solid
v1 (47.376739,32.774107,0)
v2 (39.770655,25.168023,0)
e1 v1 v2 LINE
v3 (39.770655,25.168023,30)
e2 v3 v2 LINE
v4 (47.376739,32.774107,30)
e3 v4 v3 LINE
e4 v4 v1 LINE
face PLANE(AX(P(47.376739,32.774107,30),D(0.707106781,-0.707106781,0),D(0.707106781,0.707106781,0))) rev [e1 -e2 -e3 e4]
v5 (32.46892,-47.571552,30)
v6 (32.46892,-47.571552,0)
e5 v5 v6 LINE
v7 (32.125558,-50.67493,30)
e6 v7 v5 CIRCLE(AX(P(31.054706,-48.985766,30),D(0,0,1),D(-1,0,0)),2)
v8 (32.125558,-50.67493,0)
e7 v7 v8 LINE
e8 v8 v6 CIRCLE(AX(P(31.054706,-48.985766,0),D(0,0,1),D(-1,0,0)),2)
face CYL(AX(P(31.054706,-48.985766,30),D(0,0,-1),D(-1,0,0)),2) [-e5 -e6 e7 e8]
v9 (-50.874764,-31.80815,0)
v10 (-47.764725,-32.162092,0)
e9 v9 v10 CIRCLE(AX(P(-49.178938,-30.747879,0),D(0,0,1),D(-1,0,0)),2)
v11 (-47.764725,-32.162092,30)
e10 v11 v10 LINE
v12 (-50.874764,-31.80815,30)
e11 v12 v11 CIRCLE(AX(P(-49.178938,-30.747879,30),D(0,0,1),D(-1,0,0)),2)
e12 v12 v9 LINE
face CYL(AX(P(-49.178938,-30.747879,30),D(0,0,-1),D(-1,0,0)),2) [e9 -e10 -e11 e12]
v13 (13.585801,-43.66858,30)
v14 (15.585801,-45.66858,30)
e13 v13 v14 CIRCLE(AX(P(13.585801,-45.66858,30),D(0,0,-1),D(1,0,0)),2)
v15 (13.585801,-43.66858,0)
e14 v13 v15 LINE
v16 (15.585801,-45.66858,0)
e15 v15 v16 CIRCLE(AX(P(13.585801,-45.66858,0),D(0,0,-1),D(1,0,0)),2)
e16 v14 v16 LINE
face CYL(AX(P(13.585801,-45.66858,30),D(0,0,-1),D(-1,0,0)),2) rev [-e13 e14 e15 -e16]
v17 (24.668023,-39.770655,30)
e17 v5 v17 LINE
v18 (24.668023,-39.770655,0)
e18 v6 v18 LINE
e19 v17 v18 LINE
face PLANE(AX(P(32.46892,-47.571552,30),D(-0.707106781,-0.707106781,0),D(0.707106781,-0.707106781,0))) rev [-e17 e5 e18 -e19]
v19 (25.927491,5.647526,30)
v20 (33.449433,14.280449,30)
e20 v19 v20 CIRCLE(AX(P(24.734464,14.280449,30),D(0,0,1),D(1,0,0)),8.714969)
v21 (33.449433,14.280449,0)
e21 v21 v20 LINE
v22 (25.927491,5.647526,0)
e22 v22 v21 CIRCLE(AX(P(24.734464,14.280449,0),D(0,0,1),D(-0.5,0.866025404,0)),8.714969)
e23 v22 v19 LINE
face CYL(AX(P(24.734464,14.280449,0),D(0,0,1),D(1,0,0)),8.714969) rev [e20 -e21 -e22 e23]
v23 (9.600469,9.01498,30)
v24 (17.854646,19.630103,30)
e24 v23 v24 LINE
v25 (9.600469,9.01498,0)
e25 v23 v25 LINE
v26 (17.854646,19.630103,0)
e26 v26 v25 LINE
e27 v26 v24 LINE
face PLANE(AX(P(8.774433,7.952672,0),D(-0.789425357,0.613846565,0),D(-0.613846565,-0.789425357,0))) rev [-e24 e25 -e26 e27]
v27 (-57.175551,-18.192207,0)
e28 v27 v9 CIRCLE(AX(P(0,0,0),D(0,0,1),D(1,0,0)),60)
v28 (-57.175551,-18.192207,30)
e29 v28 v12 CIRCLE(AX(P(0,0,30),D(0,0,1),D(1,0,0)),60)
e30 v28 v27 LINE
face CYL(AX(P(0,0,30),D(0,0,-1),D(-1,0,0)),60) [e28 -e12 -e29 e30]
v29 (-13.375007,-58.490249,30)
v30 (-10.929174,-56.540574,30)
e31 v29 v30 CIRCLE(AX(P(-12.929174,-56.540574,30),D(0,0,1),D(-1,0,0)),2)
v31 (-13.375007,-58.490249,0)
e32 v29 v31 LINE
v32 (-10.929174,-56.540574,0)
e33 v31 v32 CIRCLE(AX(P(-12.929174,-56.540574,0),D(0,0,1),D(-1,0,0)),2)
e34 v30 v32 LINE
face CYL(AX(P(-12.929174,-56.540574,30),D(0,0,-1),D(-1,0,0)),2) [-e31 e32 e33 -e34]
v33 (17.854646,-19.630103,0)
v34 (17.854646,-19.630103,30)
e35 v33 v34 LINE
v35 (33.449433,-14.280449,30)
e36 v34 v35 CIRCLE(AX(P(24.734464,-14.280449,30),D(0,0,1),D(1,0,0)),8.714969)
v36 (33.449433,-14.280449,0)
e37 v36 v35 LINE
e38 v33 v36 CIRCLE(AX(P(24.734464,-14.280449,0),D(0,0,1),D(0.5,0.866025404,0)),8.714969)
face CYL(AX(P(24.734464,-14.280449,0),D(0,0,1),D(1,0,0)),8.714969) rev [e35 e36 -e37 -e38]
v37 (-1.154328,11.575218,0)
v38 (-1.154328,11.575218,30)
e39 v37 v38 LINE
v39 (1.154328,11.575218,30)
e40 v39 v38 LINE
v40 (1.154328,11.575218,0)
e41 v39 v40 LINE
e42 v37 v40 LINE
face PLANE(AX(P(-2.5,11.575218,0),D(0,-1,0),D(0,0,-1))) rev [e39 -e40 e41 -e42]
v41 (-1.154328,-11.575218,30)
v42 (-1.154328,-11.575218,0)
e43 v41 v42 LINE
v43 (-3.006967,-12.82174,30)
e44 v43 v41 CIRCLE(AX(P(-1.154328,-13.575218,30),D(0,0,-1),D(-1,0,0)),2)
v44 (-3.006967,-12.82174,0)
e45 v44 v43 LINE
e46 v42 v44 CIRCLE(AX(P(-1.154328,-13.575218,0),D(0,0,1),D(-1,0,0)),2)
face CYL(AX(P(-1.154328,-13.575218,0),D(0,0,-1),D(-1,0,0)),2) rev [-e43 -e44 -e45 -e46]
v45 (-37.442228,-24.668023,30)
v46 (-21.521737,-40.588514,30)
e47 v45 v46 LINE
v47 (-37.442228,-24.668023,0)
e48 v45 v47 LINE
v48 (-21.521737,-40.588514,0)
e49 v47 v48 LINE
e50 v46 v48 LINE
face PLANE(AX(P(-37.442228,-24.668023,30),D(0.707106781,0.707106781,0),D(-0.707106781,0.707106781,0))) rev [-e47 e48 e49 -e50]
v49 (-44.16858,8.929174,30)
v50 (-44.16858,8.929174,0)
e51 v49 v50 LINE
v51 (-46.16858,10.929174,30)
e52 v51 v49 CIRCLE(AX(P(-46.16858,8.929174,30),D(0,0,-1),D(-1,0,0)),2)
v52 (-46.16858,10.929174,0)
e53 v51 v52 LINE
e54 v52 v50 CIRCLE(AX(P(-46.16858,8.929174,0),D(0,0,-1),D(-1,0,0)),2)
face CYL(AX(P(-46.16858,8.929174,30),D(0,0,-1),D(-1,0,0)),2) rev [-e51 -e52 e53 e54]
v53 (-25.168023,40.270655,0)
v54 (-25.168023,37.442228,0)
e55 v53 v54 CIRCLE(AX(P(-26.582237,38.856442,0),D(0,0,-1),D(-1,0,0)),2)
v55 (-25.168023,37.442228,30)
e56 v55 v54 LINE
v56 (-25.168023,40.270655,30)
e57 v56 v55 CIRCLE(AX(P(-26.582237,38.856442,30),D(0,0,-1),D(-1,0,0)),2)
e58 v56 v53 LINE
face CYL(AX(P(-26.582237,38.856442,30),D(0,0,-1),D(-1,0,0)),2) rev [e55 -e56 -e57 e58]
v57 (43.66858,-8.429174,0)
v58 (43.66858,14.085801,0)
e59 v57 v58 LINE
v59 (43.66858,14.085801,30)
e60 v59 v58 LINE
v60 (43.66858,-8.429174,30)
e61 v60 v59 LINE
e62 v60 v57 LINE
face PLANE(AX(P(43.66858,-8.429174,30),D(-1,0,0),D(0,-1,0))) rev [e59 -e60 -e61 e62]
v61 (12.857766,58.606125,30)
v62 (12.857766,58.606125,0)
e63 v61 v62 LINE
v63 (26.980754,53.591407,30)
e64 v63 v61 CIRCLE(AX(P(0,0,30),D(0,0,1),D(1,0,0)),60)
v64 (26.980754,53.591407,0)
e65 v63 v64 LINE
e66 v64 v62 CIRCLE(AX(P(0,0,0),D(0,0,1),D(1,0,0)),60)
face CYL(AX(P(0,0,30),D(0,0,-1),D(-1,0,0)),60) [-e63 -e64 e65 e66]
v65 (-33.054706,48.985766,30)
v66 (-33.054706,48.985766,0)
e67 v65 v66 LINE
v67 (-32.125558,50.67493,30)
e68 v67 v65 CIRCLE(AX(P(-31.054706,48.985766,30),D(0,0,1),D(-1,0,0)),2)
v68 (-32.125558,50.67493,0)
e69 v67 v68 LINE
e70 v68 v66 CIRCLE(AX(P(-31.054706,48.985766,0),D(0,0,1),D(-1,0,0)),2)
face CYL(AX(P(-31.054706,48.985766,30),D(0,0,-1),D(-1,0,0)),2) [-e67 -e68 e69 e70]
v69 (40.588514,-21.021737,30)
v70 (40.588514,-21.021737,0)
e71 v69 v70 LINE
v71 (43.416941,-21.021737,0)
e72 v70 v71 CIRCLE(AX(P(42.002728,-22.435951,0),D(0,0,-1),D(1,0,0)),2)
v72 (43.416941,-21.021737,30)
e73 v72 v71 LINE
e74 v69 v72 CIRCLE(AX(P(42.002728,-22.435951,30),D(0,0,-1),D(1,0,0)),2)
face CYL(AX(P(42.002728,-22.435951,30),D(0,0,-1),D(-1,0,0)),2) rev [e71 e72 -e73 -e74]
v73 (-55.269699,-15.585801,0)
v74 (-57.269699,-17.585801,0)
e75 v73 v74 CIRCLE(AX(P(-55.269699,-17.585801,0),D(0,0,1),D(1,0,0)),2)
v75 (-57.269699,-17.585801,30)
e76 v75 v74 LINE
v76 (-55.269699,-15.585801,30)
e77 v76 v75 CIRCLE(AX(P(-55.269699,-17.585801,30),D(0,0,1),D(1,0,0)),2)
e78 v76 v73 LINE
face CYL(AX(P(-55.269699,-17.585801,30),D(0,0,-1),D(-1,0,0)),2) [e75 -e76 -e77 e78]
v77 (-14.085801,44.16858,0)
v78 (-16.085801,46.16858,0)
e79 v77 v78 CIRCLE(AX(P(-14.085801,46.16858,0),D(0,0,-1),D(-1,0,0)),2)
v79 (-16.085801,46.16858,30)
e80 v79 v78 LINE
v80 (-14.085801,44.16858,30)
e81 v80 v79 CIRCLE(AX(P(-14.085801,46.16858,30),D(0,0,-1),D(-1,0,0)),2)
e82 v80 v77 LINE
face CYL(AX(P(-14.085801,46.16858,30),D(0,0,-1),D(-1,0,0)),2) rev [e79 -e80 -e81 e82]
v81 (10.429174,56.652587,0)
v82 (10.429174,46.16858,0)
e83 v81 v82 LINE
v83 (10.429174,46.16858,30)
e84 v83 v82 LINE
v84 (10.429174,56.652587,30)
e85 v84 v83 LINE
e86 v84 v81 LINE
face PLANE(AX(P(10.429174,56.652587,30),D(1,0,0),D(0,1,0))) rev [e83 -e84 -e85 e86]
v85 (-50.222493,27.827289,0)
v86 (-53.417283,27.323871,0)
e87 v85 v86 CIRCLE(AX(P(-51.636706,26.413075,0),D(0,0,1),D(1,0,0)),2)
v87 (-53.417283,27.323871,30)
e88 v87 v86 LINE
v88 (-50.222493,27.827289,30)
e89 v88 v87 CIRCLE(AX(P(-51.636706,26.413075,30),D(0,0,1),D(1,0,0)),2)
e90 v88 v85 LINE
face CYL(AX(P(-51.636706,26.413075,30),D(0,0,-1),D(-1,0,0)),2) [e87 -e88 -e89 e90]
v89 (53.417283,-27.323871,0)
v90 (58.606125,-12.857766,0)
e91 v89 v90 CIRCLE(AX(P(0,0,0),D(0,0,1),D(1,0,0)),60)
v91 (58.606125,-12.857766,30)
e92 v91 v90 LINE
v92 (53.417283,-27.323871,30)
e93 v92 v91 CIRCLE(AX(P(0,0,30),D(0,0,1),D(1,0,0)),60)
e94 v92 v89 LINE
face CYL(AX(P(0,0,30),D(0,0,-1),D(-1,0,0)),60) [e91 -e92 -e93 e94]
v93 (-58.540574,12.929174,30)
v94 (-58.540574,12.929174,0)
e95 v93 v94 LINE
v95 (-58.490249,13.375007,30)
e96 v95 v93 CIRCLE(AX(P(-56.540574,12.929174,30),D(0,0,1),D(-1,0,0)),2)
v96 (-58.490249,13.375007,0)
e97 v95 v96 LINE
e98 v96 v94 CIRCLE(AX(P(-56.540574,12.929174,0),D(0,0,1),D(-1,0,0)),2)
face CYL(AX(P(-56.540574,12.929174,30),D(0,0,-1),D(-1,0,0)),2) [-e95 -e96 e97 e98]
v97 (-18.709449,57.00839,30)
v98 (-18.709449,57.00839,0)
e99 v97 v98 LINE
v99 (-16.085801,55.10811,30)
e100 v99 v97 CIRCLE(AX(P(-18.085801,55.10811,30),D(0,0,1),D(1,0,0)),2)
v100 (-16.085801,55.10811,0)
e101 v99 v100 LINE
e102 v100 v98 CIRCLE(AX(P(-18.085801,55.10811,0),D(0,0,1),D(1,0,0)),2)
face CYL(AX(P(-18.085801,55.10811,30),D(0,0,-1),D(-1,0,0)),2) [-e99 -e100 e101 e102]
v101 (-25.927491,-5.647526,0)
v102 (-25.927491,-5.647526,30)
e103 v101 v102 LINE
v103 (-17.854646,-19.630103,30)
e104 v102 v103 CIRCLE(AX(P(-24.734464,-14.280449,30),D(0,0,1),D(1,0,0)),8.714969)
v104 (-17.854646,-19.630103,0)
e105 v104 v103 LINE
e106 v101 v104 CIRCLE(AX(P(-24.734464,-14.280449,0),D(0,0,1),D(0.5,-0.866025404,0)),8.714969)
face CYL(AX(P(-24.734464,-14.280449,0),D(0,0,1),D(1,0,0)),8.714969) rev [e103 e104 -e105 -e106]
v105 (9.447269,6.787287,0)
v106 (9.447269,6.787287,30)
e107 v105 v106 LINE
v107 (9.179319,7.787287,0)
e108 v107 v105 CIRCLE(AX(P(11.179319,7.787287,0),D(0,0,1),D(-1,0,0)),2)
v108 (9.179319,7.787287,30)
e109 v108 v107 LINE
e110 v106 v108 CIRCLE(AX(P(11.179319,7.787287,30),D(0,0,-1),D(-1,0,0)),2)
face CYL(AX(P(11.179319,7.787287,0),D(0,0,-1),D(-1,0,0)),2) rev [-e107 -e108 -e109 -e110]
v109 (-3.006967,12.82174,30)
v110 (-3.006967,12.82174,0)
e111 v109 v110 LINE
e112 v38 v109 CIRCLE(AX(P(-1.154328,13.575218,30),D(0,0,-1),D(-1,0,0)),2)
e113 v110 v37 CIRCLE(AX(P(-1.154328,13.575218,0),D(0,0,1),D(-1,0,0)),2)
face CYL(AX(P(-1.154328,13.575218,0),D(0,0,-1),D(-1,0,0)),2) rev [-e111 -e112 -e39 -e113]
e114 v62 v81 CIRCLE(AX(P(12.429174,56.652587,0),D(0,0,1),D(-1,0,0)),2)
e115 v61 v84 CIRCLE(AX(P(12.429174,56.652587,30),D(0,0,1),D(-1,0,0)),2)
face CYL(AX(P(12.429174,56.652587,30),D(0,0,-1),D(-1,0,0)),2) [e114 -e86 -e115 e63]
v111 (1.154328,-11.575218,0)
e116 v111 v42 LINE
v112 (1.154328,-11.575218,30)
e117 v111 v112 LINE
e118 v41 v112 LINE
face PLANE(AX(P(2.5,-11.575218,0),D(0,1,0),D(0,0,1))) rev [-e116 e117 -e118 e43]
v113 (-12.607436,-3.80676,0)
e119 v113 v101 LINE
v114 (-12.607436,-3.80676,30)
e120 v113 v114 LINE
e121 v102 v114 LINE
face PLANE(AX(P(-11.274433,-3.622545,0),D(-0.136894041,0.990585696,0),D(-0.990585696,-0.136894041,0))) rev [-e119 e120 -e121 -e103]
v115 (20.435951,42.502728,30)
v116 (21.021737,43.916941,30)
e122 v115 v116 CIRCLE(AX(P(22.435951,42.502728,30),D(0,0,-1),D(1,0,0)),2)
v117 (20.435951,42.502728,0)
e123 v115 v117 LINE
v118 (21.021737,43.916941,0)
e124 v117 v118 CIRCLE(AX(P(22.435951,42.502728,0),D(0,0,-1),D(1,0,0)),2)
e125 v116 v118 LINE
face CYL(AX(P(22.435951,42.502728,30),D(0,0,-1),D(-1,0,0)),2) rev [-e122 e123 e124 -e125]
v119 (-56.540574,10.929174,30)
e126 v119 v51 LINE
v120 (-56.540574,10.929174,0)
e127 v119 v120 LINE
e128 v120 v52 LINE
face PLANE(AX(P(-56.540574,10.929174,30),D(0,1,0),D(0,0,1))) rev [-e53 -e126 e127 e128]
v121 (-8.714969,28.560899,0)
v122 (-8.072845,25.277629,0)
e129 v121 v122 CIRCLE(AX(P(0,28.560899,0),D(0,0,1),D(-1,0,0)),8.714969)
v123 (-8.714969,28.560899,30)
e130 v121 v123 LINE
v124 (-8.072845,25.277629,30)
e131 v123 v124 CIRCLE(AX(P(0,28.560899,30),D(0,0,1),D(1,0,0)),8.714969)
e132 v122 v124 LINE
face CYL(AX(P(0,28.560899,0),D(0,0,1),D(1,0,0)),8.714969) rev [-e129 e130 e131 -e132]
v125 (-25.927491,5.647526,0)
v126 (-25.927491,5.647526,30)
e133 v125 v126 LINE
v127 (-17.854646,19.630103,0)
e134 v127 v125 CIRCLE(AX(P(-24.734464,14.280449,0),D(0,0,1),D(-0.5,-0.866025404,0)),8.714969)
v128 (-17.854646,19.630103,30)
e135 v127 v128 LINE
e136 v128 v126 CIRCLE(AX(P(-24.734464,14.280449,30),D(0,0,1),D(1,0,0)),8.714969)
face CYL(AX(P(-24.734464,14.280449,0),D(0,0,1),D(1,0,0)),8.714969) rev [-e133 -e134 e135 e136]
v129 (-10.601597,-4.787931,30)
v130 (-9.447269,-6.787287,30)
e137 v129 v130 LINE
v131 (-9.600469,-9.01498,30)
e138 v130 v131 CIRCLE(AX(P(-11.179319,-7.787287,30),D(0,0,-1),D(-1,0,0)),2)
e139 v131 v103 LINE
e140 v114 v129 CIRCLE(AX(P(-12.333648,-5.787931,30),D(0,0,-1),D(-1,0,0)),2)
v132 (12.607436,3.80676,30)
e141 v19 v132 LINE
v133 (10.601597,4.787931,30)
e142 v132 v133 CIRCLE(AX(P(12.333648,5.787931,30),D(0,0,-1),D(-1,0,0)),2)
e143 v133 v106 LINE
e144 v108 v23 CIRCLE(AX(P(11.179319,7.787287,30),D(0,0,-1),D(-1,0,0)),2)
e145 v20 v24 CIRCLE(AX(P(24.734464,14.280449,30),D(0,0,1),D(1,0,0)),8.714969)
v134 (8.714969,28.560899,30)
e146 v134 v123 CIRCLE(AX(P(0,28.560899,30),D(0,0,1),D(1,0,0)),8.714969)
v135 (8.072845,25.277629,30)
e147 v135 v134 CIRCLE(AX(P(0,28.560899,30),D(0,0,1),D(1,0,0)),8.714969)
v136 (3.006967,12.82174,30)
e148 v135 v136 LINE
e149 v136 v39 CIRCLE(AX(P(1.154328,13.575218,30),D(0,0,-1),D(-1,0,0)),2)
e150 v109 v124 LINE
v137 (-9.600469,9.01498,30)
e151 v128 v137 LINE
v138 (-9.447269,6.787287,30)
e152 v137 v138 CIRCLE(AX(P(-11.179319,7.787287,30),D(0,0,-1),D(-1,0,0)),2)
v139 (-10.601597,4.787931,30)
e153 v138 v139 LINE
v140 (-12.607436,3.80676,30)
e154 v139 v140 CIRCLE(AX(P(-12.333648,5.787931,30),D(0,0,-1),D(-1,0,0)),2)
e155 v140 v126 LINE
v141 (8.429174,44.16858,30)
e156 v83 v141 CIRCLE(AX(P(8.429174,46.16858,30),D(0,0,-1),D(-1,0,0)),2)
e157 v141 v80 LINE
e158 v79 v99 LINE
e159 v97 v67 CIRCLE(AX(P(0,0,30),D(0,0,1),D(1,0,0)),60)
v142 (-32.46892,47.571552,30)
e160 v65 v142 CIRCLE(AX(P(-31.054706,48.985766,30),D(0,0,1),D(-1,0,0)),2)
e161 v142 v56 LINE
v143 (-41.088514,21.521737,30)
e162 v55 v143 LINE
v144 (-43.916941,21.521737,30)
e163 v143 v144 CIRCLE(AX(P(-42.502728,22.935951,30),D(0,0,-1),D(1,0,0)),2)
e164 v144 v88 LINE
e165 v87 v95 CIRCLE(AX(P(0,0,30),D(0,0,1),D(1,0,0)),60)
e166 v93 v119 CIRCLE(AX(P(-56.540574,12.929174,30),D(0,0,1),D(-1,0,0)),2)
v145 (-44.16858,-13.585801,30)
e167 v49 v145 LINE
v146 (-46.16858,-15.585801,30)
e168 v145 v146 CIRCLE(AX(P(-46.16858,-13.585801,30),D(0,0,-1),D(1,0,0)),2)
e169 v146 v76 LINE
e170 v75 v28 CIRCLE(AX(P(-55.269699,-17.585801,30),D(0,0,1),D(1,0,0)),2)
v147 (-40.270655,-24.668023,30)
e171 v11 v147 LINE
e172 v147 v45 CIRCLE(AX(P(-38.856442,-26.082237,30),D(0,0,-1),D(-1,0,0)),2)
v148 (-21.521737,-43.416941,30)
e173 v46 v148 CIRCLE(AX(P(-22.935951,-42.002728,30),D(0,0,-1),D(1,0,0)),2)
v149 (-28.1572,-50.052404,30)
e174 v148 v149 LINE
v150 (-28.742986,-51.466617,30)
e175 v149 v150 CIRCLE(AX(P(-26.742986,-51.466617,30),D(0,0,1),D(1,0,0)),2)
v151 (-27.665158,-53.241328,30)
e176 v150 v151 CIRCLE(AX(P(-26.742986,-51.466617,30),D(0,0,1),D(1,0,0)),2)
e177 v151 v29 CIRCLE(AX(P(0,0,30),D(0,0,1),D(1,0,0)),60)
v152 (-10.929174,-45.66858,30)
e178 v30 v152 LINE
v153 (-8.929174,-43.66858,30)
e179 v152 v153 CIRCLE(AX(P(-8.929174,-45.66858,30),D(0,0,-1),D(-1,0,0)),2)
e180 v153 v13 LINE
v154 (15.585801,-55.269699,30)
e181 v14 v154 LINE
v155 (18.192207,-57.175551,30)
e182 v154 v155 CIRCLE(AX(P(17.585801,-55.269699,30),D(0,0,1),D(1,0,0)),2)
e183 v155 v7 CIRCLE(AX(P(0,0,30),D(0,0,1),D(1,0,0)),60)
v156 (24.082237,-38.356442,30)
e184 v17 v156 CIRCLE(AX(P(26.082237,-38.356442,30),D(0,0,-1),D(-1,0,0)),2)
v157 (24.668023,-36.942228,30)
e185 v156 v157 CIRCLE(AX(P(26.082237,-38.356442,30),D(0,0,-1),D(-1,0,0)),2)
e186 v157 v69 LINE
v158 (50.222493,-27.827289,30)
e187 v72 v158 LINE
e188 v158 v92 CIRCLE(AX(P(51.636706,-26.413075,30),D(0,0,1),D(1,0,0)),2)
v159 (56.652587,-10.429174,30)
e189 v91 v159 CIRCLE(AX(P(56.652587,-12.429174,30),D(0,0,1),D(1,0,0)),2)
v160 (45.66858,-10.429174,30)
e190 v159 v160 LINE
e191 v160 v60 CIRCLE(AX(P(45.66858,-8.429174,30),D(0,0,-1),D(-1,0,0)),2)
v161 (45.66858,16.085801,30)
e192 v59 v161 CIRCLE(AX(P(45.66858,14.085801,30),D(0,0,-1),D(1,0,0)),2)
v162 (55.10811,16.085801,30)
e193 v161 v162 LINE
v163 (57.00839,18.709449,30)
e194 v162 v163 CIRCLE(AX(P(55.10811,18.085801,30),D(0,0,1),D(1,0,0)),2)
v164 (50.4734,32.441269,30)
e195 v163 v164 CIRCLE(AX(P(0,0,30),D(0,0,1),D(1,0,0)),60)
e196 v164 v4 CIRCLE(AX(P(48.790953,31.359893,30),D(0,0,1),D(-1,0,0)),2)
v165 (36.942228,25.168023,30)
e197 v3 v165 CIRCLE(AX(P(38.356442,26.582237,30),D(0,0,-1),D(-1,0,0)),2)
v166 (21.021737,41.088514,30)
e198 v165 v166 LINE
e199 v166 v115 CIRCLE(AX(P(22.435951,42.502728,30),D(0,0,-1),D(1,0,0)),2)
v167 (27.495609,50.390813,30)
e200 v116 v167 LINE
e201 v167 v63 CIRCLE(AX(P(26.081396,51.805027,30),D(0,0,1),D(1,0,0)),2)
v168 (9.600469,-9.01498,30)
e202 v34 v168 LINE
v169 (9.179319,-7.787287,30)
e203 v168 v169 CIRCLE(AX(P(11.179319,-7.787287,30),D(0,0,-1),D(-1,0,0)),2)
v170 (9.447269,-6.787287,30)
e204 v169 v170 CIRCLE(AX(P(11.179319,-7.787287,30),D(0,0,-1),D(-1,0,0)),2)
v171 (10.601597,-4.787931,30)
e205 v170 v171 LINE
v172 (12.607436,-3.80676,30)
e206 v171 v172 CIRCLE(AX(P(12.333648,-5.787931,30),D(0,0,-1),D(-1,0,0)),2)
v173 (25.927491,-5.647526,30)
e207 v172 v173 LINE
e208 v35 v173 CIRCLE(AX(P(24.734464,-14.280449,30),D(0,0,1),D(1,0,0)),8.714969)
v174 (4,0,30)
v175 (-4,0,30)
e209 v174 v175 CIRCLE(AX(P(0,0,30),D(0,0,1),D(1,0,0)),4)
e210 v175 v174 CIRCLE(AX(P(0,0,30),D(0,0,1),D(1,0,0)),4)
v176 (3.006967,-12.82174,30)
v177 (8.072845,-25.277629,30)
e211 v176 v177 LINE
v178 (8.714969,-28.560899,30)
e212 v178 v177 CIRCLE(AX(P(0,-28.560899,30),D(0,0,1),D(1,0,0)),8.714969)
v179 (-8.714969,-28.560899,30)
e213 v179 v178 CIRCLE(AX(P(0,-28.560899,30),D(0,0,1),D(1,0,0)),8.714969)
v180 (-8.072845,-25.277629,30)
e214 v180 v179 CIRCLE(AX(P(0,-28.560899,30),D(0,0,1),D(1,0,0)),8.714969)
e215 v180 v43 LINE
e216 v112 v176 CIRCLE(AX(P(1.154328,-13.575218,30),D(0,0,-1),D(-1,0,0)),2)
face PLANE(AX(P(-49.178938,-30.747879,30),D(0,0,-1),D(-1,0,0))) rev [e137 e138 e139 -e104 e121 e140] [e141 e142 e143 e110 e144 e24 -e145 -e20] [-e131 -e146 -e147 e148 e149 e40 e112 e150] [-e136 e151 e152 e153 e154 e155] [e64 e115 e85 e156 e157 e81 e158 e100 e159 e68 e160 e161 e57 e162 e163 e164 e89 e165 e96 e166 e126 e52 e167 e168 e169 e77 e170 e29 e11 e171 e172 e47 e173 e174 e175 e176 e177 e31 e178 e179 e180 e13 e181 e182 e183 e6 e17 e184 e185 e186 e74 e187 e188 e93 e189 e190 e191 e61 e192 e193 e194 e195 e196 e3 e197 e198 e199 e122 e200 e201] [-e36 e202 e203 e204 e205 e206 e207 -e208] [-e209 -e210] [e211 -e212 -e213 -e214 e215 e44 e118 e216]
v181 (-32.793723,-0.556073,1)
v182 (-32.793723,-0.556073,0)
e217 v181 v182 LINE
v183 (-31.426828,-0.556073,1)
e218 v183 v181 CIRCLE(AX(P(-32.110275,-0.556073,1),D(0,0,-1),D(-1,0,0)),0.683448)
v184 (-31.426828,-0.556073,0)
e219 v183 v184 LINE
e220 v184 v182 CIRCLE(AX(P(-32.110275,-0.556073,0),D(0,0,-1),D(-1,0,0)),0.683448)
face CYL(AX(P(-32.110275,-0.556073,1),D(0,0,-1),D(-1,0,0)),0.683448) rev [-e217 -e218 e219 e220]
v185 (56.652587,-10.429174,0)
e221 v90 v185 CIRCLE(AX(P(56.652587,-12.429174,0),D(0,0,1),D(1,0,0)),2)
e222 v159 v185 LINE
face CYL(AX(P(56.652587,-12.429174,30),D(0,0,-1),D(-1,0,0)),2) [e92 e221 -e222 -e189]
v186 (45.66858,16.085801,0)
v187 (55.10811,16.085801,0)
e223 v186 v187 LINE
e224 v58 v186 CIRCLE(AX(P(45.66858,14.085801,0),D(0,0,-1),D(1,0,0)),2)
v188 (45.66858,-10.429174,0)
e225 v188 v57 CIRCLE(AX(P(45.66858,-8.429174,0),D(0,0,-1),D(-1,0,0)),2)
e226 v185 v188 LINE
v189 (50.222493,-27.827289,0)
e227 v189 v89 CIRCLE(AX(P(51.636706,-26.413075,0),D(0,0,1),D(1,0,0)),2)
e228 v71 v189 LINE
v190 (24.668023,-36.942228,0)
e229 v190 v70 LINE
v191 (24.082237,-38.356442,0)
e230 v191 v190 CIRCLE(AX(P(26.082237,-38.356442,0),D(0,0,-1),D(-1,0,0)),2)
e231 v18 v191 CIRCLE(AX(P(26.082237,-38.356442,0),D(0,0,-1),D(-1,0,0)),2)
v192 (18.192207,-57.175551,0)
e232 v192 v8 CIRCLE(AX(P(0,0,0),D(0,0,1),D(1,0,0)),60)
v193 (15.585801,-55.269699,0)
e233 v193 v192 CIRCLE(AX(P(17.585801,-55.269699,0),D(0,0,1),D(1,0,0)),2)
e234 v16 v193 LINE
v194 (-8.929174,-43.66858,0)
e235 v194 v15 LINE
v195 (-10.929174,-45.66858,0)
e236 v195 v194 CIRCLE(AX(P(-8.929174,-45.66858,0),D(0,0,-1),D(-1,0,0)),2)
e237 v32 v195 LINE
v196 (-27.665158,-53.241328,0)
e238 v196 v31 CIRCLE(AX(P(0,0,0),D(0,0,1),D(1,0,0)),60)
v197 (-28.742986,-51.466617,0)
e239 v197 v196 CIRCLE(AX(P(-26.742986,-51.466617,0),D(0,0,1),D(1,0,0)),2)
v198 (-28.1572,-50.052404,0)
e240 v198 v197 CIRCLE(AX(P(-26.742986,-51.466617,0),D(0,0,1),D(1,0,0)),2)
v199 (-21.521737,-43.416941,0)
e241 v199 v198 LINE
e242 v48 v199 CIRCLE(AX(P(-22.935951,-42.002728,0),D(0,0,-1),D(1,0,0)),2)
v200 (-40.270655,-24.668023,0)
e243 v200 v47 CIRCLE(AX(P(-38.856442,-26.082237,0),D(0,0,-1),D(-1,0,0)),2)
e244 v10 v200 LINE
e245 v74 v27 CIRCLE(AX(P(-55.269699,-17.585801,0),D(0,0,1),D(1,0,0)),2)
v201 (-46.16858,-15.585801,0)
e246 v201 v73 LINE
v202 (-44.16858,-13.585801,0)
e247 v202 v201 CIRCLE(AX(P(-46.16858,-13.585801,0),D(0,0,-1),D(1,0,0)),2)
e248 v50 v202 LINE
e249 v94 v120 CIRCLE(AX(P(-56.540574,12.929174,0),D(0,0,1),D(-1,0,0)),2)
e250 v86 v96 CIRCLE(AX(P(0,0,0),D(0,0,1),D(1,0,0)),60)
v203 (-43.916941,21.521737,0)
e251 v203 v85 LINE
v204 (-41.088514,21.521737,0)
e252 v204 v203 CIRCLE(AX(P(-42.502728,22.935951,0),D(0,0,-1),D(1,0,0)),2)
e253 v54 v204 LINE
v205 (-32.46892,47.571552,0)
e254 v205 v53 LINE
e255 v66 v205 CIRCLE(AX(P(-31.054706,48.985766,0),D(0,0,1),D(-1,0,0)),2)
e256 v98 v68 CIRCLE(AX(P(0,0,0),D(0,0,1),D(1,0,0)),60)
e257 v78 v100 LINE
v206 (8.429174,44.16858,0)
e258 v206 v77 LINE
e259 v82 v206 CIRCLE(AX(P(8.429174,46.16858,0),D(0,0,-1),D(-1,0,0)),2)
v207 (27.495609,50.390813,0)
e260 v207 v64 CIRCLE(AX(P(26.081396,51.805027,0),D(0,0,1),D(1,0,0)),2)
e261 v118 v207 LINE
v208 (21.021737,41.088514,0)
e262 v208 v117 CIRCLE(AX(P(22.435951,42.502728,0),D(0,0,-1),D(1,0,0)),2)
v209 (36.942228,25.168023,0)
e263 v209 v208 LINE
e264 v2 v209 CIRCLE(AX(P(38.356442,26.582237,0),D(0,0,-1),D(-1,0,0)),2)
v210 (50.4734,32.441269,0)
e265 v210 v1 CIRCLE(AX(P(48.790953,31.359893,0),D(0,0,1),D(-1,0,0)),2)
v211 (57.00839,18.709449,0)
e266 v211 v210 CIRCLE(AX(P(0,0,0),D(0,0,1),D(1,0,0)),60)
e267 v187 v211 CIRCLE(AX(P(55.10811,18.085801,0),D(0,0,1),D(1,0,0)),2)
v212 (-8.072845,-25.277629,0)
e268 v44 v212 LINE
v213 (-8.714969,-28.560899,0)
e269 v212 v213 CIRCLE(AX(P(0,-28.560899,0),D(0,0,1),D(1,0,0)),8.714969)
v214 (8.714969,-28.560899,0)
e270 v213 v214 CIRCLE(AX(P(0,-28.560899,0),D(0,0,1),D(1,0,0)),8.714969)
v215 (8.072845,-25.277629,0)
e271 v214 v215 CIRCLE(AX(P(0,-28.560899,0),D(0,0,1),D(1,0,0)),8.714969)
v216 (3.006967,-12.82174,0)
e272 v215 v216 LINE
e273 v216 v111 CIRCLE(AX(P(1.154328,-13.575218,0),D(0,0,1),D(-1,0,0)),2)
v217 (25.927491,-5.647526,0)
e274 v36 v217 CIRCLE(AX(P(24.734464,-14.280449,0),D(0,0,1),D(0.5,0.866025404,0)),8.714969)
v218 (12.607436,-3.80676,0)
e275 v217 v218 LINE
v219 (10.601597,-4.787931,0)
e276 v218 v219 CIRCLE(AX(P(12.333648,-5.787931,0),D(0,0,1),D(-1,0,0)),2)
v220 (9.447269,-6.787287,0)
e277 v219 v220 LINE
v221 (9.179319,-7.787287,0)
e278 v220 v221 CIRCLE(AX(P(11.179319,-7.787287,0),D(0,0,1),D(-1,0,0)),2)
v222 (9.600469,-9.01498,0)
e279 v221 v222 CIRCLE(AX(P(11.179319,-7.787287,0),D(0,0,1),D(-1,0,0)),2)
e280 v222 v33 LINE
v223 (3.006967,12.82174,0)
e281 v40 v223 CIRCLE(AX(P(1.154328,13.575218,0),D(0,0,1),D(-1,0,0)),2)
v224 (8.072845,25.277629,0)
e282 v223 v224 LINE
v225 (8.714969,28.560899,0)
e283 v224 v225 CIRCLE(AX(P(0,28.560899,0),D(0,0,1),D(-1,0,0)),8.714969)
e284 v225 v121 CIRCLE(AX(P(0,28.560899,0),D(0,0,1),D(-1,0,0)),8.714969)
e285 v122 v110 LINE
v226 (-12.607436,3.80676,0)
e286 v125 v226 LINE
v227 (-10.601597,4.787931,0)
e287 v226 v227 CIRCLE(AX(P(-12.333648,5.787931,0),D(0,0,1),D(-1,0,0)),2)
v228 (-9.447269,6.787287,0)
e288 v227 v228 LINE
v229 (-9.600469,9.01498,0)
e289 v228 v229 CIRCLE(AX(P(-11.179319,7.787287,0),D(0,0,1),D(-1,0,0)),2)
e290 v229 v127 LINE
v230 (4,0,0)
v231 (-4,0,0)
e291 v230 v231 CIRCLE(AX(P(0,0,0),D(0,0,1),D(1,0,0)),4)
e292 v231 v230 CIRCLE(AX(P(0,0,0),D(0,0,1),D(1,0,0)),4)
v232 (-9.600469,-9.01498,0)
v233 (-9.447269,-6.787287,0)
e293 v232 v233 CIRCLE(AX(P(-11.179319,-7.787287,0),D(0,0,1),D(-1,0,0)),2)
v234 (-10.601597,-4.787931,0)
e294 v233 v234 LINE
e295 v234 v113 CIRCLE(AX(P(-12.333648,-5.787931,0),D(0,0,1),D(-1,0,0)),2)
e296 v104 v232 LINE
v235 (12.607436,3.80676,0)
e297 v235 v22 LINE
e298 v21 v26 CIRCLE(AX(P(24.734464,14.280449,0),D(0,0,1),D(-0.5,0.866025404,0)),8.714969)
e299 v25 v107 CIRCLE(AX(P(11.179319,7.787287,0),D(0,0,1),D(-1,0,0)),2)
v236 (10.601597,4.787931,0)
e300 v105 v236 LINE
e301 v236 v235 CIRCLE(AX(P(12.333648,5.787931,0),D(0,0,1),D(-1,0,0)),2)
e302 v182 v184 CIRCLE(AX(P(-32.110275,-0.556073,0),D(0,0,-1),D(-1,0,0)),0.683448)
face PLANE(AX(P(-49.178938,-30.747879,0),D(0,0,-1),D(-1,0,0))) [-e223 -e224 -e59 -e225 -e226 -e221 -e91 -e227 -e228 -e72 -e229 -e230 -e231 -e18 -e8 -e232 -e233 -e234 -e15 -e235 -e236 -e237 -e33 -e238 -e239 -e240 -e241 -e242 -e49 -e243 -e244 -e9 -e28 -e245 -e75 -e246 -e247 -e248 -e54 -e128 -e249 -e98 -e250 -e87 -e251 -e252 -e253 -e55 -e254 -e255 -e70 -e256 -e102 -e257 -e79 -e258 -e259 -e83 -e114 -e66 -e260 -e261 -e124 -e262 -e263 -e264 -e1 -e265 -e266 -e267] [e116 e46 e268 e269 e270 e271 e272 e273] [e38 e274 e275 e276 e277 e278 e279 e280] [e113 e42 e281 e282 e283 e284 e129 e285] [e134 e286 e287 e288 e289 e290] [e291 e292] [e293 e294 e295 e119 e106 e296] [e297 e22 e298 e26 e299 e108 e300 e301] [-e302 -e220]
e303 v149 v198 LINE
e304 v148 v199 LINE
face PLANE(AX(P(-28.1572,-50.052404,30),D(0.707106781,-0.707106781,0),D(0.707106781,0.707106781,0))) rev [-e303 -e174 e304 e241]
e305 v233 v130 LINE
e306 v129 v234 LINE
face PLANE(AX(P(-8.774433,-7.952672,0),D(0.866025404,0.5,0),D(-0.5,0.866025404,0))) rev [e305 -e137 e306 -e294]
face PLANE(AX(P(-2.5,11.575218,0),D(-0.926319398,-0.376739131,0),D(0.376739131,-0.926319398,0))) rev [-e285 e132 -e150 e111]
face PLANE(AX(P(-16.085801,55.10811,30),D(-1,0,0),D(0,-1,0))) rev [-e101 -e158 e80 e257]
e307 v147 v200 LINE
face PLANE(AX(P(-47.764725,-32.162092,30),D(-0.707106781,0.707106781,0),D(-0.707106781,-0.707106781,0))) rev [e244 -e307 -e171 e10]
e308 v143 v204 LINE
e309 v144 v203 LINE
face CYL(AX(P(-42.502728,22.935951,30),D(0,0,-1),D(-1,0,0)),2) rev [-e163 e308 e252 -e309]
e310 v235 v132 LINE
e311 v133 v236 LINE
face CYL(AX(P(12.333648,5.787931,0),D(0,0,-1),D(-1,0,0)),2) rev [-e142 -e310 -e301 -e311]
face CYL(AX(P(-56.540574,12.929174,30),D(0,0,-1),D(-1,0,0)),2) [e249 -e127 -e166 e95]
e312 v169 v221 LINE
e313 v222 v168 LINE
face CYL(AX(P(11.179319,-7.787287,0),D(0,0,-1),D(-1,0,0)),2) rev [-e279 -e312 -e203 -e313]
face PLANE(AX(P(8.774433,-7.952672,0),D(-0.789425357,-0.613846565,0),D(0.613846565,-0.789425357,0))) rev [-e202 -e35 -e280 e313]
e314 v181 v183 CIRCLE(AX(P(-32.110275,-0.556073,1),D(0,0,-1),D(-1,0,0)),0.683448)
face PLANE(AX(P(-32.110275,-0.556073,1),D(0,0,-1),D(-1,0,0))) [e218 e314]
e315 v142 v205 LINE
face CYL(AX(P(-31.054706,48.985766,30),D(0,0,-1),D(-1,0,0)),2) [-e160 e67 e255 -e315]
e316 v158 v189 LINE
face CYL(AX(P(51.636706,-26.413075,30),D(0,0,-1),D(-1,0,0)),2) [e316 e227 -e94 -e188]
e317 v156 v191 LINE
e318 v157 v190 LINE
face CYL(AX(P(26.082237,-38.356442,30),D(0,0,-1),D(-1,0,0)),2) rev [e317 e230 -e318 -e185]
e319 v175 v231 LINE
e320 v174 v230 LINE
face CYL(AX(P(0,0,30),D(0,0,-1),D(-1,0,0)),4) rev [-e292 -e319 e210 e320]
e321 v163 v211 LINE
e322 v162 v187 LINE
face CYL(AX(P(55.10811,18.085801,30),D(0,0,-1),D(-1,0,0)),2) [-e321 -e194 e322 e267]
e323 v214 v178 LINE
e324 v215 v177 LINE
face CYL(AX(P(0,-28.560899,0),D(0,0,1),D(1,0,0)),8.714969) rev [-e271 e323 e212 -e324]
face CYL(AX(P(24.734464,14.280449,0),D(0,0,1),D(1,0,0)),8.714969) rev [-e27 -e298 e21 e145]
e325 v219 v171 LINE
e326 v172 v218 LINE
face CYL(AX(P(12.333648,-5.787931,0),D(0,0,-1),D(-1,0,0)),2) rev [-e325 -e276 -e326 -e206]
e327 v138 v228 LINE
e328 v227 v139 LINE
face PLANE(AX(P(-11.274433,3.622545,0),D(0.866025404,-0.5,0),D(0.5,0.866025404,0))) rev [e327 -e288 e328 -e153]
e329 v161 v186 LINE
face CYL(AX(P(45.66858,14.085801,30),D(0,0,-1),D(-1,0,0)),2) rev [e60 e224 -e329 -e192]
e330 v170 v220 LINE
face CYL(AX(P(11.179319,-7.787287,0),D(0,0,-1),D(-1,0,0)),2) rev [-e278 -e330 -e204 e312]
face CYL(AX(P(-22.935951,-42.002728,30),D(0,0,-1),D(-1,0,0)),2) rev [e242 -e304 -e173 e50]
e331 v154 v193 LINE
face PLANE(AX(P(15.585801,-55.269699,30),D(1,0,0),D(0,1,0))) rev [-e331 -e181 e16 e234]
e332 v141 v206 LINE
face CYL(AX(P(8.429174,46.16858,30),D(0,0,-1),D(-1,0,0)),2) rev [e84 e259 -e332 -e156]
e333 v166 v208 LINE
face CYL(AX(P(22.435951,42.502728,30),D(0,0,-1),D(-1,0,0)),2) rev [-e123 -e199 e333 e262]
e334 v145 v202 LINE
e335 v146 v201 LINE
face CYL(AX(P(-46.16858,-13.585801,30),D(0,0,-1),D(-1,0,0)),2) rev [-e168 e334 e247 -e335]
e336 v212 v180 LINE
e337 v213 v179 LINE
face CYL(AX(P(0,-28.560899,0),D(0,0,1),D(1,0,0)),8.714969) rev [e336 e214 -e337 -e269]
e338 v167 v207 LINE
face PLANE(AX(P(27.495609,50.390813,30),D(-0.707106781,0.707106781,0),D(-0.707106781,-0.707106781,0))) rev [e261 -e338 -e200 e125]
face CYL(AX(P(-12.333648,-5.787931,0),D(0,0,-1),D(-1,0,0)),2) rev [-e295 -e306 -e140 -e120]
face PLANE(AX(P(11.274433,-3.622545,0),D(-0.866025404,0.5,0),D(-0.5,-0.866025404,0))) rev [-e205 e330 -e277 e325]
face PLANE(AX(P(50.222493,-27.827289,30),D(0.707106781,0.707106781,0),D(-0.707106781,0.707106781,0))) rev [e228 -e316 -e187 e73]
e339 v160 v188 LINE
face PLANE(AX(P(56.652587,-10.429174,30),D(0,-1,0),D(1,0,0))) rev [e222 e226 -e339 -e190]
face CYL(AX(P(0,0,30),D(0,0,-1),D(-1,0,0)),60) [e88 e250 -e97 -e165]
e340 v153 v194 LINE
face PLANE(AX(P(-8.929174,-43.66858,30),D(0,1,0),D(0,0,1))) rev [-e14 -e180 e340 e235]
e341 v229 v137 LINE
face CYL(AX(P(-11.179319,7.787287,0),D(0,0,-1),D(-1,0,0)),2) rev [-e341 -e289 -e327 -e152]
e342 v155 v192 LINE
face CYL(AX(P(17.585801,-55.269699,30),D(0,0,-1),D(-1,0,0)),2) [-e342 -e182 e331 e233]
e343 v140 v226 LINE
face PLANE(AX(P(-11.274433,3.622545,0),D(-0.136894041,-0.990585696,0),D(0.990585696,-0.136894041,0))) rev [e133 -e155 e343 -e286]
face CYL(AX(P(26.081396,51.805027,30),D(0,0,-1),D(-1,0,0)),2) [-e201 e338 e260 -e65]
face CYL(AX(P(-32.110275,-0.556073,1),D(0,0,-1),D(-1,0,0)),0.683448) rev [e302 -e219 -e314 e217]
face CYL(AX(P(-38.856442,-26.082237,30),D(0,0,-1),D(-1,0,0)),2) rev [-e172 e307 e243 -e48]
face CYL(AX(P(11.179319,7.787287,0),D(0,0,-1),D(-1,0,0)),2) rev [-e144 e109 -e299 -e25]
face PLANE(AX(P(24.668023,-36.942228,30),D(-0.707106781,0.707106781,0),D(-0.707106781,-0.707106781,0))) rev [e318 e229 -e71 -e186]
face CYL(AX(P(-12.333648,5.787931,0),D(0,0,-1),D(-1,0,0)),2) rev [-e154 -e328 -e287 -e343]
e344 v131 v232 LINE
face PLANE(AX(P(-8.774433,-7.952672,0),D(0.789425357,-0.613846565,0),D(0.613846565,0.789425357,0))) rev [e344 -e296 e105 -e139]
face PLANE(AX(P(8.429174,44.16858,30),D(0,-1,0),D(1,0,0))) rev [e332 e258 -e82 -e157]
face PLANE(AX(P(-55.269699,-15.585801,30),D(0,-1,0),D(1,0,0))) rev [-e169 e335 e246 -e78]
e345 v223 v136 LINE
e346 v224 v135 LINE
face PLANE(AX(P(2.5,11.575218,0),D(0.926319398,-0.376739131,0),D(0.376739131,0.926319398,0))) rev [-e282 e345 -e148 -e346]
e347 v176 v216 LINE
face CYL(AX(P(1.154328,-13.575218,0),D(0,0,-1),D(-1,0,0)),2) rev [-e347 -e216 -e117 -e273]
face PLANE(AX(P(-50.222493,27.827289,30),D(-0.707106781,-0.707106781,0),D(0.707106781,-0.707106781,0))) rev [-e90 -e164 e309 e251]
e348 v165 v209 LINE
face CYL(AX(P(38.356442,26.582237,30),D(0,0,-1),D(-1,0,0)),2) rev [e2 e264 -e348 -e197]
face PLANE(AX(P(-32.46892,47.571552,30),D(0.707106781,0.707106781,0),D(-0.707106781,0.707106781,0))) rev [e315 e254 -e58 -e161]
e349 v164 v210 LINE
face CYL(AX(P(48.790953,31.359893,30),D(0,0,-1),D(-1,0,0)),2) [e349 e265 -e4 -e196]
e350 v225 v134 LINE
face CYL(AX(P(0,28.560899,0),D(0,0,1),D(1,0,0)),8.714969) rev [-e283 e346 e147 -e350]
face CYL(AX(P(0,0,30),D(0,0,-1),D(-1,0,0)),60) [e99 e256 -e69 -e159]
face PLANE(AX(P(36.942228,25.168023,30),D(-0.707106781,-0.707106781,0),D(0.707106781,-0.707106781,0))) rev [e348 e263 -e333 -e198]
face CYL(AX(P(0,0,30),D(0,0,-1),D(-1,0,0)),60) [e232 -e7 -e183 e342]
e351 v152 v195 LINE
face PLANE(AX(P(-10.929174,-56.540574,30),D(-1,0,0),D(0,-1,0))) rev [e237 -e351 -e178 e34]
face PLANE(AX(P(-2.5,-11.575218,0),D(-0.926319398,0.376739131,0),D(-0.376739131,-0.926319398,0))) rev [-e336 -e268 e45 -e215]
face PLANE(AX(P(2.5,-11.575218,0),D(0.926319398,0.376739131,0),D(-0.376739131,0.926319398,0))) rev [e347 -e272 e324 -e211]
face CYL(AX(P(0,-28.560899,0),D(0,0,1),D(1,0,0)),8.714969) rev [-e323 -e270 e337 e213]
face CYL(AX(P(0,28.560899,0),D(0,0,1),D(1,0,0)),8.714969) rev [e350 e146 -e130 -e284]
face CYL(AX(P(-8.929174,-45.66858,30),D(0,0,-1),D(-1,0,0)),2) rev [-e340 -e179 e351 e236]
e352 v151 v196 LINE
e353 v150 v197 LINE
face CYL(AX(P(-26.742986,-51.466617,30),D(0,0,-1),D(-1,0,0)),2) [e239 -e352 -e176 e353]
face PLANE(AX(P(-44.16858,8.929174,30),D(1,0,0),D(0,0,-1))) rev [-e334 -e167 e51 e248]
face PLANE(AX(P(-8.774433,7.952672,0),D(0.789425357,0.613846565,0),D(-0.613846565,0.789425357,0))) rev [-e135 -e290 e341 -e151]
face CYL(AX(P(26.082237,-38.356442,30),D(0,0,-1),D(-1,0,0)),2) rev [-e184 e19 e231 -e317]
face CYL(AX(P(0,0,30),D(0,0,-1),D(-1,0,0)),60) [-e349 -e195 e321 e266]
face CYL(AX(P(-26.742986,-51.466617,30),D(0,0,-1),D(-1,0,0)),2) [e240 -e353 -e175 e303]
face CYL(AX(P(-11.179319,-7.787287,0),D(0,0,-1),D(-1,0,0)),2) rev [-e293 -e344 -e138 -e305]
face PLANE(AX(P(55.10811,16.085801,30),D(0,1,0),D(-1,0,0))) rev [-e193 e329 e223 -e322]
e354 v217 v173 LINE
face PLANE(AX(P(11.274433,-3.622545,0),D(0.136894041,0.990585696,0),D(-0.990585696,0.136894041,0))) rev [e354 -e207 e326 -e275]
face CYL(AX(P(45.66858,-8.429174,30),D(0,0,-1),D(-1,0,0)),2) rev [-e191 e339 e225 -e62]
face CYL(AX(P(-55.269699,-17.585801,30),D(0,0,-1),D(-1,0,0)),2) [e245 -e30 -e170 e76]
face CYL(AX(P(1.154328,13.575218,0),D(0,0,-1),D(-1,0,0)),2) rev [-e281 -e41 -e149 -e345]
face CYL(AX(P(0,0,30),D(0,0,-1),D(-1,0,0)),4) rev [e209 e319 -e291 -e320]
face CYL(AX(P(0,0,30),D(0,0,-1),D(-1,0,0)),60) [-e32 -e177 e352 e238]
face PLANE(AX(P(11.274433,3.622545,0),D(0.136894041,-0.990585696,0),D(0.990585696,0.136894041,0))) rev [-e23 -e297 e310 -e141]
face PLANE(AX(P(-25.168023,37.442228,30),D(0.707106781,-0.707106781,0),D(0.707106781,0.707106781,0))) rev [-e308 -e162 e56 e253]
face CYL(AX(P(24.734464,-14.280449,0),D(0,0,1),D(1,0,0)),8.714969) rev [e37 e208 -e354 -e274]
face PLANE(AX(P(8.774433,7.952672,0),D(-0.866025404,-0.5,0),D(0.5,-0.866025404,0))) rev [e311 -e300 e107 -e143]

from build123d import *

# Parameters (mm, degrees)
SKETCH1_R                = 4
BOSS_EXTRUDE2_DEPTH      = 30
CUT_EXTRUDE2_DEPTH       = 89.20573662
FILLET1_R                = 2
CIRPATTERN1_COUNT        = 6
FILLET1_OF_CIRPATTERN1_R = 2
SKETCH12_R               = 0.68344787
CUT_EXTRUDE4_DEPTH       = 1


with BuildPart() as part:
    # Sketch1 → Boss-Extrude2 (new body)
    with BuildSketch(Plane.XY):
        with BuildLine():
            Line((10.429173845, 56.65258721), (10.429173845, 46.168579918))
            ThreePointArc((10.429173845, 46.168579918), (9.843387407, 44.754366355), (8.429173845, 44.168579918))
            Line((8.429173845, 44.168579918), (-14.085800573, 44.168579918))
            ThreePointArc((-14.085800573, 44.168579918), (-15.500014135, 44.754366355), (-16.085800573, 46.168579918))
            Line((-16.085800573, 46.168579918), (-16.085800573, 55.108110271))
            ThreePointArc((-16.085800573, 55.108110271), (-16.912620406, 56.727878247), (-18.709448869, 57.008389935))
            ThreePointArc((-18.709448869, 57.008389935), (-25.61401293, 54.257924229), (-32.125557949, 50.67492996))
            ThreePointArc((-32.125557949, 50.67492996), (-33.042575786, 49.205706038), (-32.46891958, 47.571552066))
            Line((-32.46891958, 47.571552066), (-25.168022999, 40.270655485))
            ThreePointArc((-25.168022999, 40.270655485), (-24.582236562, 38.856441923), (-25.168022999, 37.44222836))
            Line((-25.168022999, 37.44222836), (-41.088514088, 21.521737271))
            ThreePointArc((-41.088514088, 21.521737271), (-42.50272765, 20.935950834), (-43.916941213, 21.521737271))
            Line((-43.916941213, 21.521737271), (-50.22249286, 27.827288919))
            ThreePointArc((-50.22249286, 27.827288919), (-51.948014566, 28.38869861), (-53.417282506, 27.323871059))
            ThreePointArc((-53.417282506, 27.323871059), (-56.386758875, 20.506911606), (-58.490248558, 13.375007425))
            ThreePointArc((-58.490248558, 13.375007425), (-58.10448971, 11.682511734), (-56.540573606, 10.929173845))
            Line((-56.540573606, 10.929173845), (-46.168579918, 10.929173845))
            ThreePointArc((-46.168579918, 10.929173845), (-44.754366355, 10.343387407), (-44.168579918, 8.929173845))
            Line((-44.168579918, 8.929173845), (-44.168579918, -13.585800573))
            ThreePointArc((-44.168579918, -13.585800573), (-44.754366355, -15.000014135), (-46.168579918, -15.585800573))
            Line((-46.168579918, -15.585800573), (-55.269698915, -15.585800573))
            ThreePointArc((-55.269698915, -15.585800573), (-56.884135943, -16.405295137), (-57.175550602, -18.192207489))
            ThreePointArc((-57.175550602, -18.192207489), (-54.452420305, -25.197895208), (-50.874763654, -31.808150263))
            ThreePointArc((-50.874763654, -31.808150263), (-49.405090867, -32.735051195), (-47.764724636, -32.16209215))
            Line((-47.764724636, -32.16209215), (-40.270655485, -24.668022999))
            ThreePointArc((-40.270655485, -24.668022999), (-38.856441923, -24.082236562), (-37.44222836, -24.668022999))
            Line((-37.44222836, -24.668022999), (-21.521737271, -40.588514088))
            ThreePointArc((-21.521737271, -40.588514088), (-20.935950834, -42.00272765), (-21.521737271, -43.416941213))
            Line((-21.521737271, -43.416941213), (-28.157199739, -50.05240368))
            ThreePointArc((-28.157199739, -50.05240368), (-28.719595437, -51.771602209), (-27.665158113, -53.241328182))
            ThreePointArc((-27.665158113, -53.241328182), (-20.687232491, -56.320852372), (-13.375007425, -58.490248558))
            ThreePointArc((-13.375007425, -58.490248558), (-11.682511734, -58.10448971), (-10.929173845, -56.540573606))
            Line((-10.929173845, -56.540573606), (-10.929173845, -45.668579918))
            ThreePointArc((-10.929173845, -45.668579918), (-10.343387407, -44.254366355), (-8.929173845, -43.668579918))
            Line((-8.929173845, -43.668579918), (13.585800573, -43.668579918))
            ThreePointArc((13.585800573, -43.668579918), (15.000014135, -44.254366355), (15.585800573, -45.668579918))
            Line((15.585800573, -45.668579918), (15.585800573, -55.269698915))
            ThreePointArc((15.585800573, -55.269698915), (16.405295137, -56.884135943), (18.192207489, -57.175550602))
            ThreePointArc((18.192207489, -57.175550602), (25.3679699, -54.373395178), (32.125557949, -50.67492996))
            ThreePointArc((32.125557949, -50.67492996), (33.042575786, -49.205706038), (32.46891958, -47.571552066))
            Line((32.46891958, -47.571552066), (24.668022999, -39.770655485))
            ThreePointArc((24.668022999, -39.770655485), (24.082236562, -38.356441923), (24.668022999, -36.94222836))
            Line((24.668022999, -36.94222836), (40.588514088, -21.021737271))
            ThreePointArc((40.588514088, -21.021737271), (42.00272765, -20.435950834), (43.416941213, -21.021737271))
            Line((43.416941213, -21.021737271), (50.22249286, -27.827288919))
            ThreePointArc((50.22249286, -27.827288919), (51.948014566, -28.38869861), (53.417282506, -27.323871059))
            ThreePointArc((53.417282506, -27.323871059), (56.476791597, -20.257640804), (58.6061247, -12.857766046))
            ThreePointArc((58.6061247, -12.857766046), (58.210981319, -11.175615789), (56.65258721, -10.429173845))
            Line((56.65258721, -10.429173845), (45.668579918, -10.429173845))
            ThreePointArc((45.668579918, -10.429173845), (44.254366355, -9.843387407), (43.668579918, -8.429173845))
            Line((43.668579918, -8.429173845), (43.668579918, 14.085800573))
            ThreePointArc((43.668579918, 14.085800573), (44.254366355, 15.500014135), (45.668579918, 16.085800573))
            Line((45.668579918, 16.085800573), (55.108110271, 16.085800573))
            ThreePointArc((55.108110271, 16.085800573), (56.727878247, 16.912620406), (57.008389935, 18.709448869))
            ThreePointArc((57.008389935, 18.709448869), (54.177712128, 25.783240847), (50.473399603, 32.441268972))
            ThreePointArc((50.473399603, 32.441268972), (49.004687645, 33.348439914), (47.376739387, 32.774106902))
            Line((47.376739387, 32.774106902), (39.770655485, 25.168022999))
            ThreePointArc((39.770655485, 25.168022999), (38.356441923, 24.582236562), (36.94222836, 25.168022999))
            Line((36.94222836, 25.168022999), (21.021737271, 41.088514088))
            ThreePointArc((21.021737271, 41.088514088), (20.435950834, 42.50272765), (21.021737271, 43.916941213))
            Line((21.021737271, 43.916941213), (27.495609263, 50.390813204))
            ThreePointArc((27.495609263, 50.390813204), (28.056010613, 52.122667993), (26.980754173, 53.591407))
            ThreePointArc((26.980754173, 53.591407), (20.076448185, 56.541455838), (12.857766046, 58.6061247))
            ThreePointArc((12.857766046, 58.6061247), (11.175615789, 58.210981319), (10.429173845, 56.65258721))
        make_face()
        Circle(SKETCH1_R, mode=Mode.SUBTRACT)
    extrude(amount=BOSS_EXTRUDE2_DEPTH)

    # Sketch2 → Cut-Extrude2 (cut, symmetric)
    with BuildSketch(Plane.XY.offset(30)):
        with BuildLine():
            Line((-2.5, 11.575217828), (2.5, 11.575217828))
            Line((2.5, 11.575217828), (8.072844982, 25.27762882))
            ThreePointArc((8.072844982, 25.27762882), (0, 37.27586788), (-8.072844982, 25.27762882))
            Line((-8.072844982, 25.27762882), (-2.5, 11.575217828))
        make_face()
    cut_extrude2 = extrude(amount=CUT_EXTRUDE2_DEPTH, both=True, mode=Mode.SUBTRACT)

    # Fillet1
    fillet1_edges = [part.edges().sort_by_distance(p)[0] for p in [
        (-2.5, 11.575217828, 15),
        (2.5, 11.575217828, 15),
    ]]
    fillet(fillet1_edges, radius=FILLET1_R)

    # CirPattern1: Cut-Extrude2 ×6 about axis
    cirpattern1_axis = Axis((0, 0, 0), (0, 0, 1))
    for i in range(1, CIRPATTERN1_COUNT):
        add(cut_extrude2.rotate(cirpattern1_axis, i * 360 / CIRPATTERN1_COUNT), mode=Mode.SUBTRACT)

    # Fillet1 of CirPattern1
    fillet1_of_cirpattern1_edges = [part.edges().sort_by_distance(p)[0] for p in [
        (-11.274432693, 3.622545404, 15),
        (-8.774432693, 7.952672423, 15),
        (-8.774432693, -7.952672423, 15),
        (-11.274432693, -3.622545404, 15),
        (2.5, -11.575217828, 15),
        (-2.5, -11.575217828, 15),
        (11.274432693, -3.622545404, 15),
        (8.774432693, -7.952672423, 15),
        (8.774432693, 7.952672423, 15),
        (11.274432693, 3.622545404, 15),
    ]]
    fillet(fillet1_of_cirpattern1_edges, radius=FILLET1_OF_CIRPATTERN1_R)

    # Sketch12 → Cut-Extrude4 (cut)
    with BuildSketch(Plane(origin=(0, 0, 0), x_dir=(-1, 0, 0), z_dir=(0, 0, -1))):
        with Locations((32.110275417, -0.556072549)):
            Circle(SKETCH12_R)
    extrude(amount=-CUT_EXTRUDE4_DEPTH, mode=Mode.SUBTRACT)


solid = part.part
